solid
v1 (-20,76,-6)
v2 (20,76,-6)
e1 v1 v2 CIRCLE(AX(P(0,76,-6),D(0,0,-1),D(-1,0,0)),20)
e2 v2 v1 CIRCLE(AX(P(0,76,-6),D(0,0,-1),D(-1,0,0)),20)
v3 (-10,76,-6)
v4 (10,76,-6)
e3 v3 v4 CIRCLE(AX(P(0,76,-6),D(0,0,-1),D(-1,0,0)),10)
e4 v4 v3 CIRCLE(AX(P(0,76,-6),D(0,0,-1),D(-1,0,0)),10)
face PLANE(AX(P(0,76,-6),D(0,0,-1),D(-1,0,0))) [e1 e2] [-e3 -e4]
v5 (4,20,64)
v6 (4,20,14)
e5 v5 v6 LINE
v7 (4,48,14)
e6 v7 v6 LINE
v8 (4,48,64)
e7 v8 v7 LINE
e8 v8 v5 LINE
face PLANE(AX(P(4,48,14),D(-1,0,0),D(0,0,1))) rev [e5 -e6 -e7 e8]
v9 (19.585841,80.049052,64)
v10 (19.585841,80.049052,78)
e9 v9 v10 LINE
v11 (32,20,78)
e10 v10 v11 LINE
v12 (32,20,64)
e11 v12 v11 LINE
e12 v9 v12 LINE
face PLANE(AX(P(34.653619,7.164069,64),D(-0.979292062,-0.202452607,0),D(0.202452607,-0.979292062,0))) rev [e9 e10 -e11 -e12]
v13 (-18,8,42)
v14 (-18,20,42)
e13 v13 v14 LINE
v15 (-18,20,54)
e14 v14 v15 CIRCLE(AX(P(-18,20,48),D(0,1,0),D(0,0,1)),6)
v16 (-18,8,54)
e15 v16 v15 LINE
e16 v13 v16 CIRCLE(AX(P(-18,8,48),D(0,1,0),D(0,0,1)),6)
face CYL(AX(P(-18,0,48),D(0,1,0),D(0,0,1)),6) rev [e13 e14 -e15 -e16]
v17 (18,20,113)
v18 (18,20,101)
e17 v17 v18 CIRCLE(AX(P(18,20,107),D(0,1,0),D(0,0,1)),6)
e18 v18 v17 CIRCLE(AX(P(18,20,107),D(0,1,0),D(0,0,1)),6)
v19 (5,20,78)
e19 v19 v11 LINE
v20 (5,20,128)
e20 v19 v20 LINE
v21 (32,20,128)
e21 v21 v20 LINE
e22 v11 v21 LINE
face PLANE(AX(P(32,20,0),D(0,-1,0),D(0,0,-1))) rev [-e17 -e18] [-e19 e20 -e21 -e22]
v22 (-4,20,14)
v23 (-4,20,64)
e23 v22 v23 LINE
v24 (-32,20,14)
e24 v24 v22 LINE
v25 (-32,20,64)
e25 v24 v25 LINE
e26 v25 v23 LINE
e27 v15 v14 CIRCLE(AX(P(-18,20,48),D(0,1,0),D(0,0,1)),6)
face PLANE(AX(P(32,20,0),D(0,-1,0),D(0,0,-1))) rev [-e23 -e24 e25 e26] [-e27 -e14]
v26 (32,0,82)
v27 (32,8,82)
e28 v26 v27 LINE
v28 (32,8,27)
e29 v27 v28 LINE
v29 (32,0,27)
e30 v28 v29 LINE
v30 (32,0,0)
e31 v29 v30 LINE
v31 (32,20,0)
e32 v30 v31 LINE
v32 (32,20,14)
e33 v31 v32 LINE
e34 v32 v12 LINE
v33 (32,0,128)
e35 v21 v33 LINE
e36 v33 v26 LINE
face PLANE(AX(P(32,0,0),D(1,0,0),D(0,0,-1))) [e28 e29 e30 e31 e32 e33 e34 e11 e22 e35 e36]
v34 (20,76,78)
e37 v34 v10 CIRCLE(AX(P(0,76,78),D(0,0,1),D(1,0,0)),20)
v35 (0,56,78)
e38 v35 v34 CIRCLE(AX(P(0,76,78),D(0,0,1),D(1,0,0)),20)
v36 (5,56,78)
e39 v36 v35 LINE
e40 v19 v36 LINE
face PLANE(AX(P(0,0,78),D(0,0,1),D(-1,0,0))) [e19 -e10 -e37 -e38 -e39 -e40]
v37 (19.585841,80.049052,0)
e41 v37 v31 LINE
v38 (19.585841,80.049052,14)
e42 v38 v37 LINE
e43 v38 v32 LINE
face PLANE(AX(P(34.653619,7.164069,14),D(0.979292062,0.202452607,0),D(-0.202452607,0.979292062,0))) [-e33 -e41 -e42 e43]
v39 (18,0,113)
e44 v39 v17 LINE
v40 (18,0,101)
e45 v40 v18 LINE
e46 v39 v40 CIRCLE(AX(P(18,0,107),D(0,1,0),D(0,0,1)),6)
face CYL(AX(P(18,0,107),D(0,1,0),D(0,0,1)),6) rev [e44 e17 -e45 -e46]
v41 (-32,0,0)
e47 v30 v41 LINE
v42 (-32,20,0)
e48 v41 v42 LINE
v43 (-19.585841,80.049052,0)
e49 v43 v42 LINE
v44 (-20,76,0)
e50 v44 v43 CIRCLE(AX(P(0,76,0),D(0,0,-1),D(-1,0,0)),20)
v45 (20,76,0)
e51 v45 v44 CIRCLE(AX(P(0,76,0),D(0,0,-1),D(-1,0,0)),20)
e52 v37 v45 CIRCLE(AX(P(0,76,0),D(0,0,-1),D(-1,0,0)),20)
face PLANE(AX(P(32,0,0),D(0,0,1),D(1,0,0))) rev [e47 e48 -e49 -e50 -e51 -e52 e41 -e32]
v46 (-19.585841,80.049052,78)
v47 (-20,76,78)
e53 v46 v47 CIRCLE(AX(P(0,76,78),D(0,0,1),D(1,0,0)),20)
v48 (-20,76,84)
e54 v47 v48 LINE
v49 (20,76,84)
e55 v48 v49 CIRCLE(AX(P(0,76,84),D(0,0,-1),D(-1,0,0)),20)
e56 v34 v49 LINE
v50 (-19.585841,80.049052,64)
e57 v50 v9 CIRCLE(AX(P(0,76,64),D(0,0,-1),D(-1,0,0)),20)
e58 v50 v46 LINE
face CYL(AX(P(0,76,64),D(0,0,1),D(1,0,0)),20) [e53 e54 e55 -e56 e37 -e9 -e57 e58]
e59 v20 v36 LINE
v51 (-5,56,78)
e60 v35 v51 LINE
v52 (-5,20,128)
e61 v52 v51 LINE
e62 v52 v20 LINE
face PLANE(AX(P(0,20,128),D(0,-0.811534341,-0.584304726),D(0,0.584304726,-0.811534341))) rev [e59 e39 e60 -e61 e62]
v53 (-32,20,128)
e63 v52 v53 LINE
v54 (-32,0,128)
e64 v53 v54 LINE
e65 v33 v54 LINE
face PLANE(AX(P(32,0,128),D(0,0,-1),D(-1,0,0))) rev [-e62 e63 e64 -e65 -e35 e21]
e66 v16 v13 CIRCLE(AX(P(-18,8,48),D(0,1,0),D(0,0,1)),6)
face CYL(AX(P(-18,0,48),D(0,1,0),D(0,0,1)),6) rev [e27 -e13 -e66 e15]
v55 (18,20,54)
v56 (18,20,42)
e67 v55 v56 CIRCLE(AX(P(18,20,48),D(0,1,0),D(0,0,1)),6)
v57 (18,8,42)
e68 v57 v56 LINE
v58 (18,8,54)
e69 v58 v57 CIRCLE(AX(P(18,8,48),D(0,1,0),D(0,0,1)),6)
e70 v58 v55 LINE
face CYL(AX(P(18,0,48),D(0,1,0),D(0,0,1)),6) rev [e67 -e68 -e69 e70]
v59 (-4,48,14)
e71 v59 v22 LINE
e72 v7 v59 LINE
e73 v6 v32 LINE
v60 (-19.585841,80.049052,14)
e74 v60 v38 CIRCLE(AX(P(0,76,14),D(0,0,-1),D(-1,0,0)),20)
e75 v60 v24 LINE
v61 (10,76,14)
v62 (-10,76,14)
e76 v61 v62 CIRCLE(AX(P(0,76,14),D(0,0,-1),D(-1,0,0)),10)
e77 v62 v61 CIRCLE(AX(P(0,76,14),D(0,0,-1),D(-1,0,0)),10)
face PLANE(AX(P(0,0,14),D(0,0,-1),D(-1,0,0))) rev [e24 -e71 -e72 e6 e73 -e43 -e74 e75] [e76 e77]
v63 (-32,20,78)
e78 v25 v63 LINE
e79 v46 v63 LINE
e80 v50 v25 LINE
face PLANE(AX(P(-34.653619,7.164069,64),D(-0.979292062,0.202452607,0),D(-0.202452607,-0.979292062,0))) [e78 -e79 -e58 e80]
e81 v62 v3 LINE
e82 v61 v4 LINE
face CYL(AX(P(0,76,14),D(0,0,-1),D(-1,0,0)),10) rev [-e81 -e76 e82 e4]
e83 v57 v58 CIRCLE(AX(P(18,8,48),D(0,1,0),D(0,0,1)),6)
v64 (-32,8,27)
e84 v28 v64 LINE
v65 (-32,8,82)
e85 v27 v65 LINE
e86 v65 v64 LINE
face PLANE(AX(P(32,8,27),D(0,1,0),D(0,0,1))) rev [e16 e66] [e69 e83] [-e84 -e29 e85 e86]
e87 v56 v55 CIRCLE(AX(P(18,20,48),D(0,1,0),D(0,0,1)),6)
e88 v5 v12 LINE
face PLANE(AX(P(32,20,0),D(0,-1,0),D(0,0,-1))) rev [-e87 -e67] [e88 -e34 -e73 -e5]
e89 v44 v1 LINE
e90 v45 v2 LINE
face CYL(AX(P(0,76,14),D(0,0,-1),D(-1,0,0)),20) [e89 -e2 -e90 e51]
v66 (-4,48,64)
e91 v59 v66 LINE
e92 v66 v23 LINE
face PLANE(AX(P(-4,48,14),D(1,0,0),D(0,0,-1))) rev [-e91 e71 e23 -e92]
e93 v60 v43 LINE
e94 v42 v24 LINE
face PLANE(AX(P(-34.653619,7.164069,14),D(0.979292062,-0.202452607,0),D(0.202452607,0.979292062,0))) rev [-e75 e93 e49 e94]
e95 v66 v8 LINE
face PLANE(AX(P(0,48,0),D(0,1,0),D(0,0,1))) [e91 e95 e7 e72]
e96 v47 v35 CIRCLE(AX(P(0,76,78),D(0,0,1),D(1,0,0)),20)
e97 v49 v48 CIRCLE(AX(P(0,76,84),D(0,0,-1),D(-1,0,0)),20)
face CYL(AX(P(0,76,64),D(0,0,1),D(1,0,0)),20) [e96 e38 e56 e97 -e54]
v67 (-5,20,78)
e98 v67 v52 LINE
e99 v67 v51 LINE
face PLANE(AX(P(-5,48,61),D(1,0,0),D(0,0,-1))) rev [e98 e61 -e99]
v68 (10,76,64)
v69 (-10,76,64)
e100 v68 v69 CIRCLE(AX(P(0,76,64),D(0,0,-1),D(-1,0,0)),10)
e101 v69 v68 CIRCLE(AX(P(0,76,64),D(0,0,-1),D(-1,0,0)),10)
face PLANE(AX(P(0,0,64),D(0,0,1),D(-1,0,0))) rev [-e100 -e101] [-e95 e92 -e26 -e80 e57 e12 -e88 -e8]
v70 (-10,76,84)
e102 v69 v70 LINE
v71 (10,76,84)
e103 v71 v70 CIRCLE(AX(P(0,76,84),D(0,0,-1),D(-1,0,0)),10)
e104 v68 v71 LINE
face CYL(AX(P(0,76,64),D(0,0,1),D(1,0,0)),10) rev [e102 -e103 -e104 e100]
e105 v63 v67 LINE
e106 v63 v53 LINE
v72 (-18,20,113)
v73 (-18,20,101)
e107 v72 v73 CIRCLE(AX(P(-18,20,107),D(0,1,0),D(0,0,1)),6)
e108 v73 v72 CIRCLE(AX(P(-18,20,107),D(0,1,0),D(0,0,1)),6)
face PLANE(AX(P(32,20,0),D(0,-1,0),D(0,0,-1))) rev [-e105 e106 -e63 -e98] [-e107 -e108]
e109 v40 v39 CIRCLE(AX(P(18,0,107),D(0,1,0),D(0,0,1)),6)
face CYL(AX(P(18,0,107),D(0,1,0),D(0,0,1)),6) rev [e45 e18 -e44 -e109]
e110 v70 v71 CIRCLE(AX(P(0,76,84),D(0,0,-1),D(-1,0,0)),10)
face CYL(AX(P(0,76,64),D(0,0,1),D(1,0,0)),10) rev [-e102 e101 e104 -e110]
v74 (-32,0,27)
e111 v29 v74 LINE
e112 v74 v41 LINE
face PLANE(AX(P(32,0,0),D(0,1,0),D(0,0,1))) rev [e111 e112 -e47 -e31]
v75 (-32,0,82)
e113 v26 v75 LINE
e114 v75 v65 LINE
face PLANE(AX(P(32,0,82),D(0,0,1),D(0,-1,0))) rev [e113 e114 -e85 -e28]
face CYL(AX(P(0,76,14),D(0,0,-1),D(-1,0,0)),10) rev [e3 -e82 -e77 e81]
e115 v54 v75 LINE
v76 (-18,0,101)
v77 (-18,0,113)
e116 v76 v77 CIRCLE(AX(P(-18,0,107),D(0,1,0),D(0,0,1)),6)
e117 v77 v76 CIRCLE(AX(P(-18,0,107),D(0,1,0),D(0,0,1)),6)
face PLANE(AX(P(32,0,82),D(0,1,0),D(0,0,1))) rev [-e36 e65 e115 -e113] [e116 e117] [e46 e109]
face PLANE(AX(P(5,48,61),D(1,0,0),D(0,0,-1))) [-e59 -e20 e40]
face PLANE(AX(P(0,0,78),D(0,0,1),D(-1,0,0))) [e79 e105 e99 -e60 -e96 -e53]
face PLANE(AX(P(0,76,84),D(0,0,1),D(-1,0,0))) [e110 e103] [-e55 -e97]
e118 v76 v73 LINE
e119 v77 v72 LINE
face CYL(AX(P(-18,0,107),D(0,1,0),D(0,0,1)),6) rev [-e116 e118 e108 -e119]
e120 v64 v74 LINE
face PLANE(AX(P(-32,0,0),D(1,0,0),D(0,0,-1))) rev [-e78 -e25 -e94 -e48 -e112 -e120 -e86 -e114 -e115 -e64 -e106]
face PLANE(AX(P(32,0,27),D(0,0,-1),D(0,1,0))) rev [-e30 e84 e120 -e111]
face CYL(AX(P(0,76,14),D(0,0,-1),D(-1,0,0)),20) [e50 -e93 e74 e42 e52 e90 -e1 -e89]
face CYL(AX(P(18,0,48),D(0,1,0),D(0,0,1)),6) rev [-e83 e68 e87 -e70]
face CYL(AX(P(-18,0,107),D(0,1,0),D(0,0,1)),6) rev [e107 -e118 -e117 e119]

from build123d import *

# Parameters (mm, degrees)
BASE_PLATE_DEPTH           = 32
LUG_UPRIGHT_PROFILE_R      = 10
LUG_UPRIGHT_DEPTH          = 14
LUG_START                  = 6
SKETCH2_3_R                = 20
SKETCH2_3_R_2              = 10
LUG_HUB_BOSS_DEPTH         = 6
BACK_WEB_PROFILE_W         = 8
BACK_WEB_PROFILE_H         = 50
BACK_WEB_DEPTH             = 28
STIFFENING_RIB_REACH       = 165.169
STIFFENING_RIB_PATH_WALL_W = 389.948936072
STIFFENING_RIB_PATH_WALL_H = 10
MOUNTING_HOLES_PROFILE_R   = 6
MOUNTING_HOLES_DEPTH       = 153.262930485


with BuildPart() as part:
    # Base Plate Profile → Base Plate (new, symmetric)
    with BuildSketch(Plane(origin=(0, 0, 0), x_dir=(0, 0, -1), z_dir=(1, 0, 0))):
        Polygon((-82, 0), (-128, 0), (-128, 20), (0, 20), (0, 0), (-27, 0), (-27, 8), (-82, 8), align=None)
    extrude(amount=BASE_PLATE_DEPTH, both=True)

    # Lug Upright Profile → Lug Upright (add)
    with BuildSketch(Plane(origin=(0, 0, 0), x_dir=(-1, 0, 0), z_dir=(0, 0, -1))):
        with BuildLine():
            Line((-19.585841233, 80.049052133), (-32, 20))
            Line((-32, 20), (32, 20))
            Line((32, 20), (19.585841233, 80.049052133))
            ThreePointArc((19.585841233, 80.049052133), (0, 96), (-19.585841233, 80.049052133))
        make_face()
        with Locations((0, 76)):
            Circle(LUG_UPRIGHT_PROFILE_R, mode=Mode.SUBTRACT)
    lug_upright = extrude(amount=-LUG_UPRIGHT_DEPTH)

    # Sketch2_3 → Lug Hub Boss (add)
    with BuildSketch(Plane(origin=(0, 0, 0), x_dir=(-1, 0, 0), z_dir=(0, 0, -1)).offset(LUG_START)):
        with Locations((0, 76)):
            Circle(SKETCH2_3_R)
        with Locations((0, 76)):
            Circle(SKETCH2_3_R_2, mode=Mode.SUBTRACT)
    lug_hub_boss = extrude(amount=-LUG_HUB_BOSS_DEPTH)

    # Lug Mirror: Lug Upright, Lug Hub Boss across plane
    add(lug_upright.mirror(Plane.XY.offset(39)))
    add(lug_hub_boss.mirror(Plane.XY.offset(39)))

    # Back Web Profile → Back Web (add)
    with BuildSketch(Plane(origin=(0, 20, 0), x_dir=(1, 0, 0), z_dir=(0, 1, 0))):
        with Locations((0, -39)):
            Rectangle(BACK_WEB_PROFILE_W, BACK_WEB_PROFILE_H)
    extrude(amount=BACK_WEB_DEPTH)

    # Stiffening Rib Path wall → Stiffening Rib (add, up to next)
    with BuildSketch(Plane(origin=(0, 38, 103), x_dir=(0, 0.584304725845, -0.811534341451), z_dir=(0, 0.811534341451, 0.584304725845)), mode=Mode.PRIVATE) as stiffening_rib_sk1:
        Rectangle(STIFFENING_RIB_PATH_WALL_W, STIFFENING_RIB_PATH_WALL_H)
    stiffening_rib_tool1 = extrude(stiffening_rib_sk1.sketch, amount=-STIFFENING_RIB_REACH, mode=Mode.PRIVATE) - part.part
    add(stiffening_rib_tool1.solids().sort_by_distance((0, 38, 103))[0])

    # Mounting Holes Profile → Mounting Holes (cut, through all)
    with BuildSketch(Plane(origin=(0, 20, 0), x_dir=(1, 0, 0), z_dir=(0, 1, 0))):
        with Locations(Location((-18, -48, 0), (0, 0, 270))):
            Circle(MOUNTING_HOLES_PROFILE_R)
        with Locations(Location((18, -48, 0), (0, 0, 270))):
            Circle(MOUNTING_HOLES_PROFILE_R)
        with Locations(Location((18, -107, 0), (0, 0, 270))):
            Circle(MOUNTING_HOLES_PROFILE_R)
        with Locations(Location((-18, -107, 0), (0, 0, 270))):
            Circle(MOUNTING_HOLES_PROFILE_R)
    extrude(amount=-MOUNTING_HOLES_DEPTH, mode=Mode.SUBTRACT)


solid = part.part
